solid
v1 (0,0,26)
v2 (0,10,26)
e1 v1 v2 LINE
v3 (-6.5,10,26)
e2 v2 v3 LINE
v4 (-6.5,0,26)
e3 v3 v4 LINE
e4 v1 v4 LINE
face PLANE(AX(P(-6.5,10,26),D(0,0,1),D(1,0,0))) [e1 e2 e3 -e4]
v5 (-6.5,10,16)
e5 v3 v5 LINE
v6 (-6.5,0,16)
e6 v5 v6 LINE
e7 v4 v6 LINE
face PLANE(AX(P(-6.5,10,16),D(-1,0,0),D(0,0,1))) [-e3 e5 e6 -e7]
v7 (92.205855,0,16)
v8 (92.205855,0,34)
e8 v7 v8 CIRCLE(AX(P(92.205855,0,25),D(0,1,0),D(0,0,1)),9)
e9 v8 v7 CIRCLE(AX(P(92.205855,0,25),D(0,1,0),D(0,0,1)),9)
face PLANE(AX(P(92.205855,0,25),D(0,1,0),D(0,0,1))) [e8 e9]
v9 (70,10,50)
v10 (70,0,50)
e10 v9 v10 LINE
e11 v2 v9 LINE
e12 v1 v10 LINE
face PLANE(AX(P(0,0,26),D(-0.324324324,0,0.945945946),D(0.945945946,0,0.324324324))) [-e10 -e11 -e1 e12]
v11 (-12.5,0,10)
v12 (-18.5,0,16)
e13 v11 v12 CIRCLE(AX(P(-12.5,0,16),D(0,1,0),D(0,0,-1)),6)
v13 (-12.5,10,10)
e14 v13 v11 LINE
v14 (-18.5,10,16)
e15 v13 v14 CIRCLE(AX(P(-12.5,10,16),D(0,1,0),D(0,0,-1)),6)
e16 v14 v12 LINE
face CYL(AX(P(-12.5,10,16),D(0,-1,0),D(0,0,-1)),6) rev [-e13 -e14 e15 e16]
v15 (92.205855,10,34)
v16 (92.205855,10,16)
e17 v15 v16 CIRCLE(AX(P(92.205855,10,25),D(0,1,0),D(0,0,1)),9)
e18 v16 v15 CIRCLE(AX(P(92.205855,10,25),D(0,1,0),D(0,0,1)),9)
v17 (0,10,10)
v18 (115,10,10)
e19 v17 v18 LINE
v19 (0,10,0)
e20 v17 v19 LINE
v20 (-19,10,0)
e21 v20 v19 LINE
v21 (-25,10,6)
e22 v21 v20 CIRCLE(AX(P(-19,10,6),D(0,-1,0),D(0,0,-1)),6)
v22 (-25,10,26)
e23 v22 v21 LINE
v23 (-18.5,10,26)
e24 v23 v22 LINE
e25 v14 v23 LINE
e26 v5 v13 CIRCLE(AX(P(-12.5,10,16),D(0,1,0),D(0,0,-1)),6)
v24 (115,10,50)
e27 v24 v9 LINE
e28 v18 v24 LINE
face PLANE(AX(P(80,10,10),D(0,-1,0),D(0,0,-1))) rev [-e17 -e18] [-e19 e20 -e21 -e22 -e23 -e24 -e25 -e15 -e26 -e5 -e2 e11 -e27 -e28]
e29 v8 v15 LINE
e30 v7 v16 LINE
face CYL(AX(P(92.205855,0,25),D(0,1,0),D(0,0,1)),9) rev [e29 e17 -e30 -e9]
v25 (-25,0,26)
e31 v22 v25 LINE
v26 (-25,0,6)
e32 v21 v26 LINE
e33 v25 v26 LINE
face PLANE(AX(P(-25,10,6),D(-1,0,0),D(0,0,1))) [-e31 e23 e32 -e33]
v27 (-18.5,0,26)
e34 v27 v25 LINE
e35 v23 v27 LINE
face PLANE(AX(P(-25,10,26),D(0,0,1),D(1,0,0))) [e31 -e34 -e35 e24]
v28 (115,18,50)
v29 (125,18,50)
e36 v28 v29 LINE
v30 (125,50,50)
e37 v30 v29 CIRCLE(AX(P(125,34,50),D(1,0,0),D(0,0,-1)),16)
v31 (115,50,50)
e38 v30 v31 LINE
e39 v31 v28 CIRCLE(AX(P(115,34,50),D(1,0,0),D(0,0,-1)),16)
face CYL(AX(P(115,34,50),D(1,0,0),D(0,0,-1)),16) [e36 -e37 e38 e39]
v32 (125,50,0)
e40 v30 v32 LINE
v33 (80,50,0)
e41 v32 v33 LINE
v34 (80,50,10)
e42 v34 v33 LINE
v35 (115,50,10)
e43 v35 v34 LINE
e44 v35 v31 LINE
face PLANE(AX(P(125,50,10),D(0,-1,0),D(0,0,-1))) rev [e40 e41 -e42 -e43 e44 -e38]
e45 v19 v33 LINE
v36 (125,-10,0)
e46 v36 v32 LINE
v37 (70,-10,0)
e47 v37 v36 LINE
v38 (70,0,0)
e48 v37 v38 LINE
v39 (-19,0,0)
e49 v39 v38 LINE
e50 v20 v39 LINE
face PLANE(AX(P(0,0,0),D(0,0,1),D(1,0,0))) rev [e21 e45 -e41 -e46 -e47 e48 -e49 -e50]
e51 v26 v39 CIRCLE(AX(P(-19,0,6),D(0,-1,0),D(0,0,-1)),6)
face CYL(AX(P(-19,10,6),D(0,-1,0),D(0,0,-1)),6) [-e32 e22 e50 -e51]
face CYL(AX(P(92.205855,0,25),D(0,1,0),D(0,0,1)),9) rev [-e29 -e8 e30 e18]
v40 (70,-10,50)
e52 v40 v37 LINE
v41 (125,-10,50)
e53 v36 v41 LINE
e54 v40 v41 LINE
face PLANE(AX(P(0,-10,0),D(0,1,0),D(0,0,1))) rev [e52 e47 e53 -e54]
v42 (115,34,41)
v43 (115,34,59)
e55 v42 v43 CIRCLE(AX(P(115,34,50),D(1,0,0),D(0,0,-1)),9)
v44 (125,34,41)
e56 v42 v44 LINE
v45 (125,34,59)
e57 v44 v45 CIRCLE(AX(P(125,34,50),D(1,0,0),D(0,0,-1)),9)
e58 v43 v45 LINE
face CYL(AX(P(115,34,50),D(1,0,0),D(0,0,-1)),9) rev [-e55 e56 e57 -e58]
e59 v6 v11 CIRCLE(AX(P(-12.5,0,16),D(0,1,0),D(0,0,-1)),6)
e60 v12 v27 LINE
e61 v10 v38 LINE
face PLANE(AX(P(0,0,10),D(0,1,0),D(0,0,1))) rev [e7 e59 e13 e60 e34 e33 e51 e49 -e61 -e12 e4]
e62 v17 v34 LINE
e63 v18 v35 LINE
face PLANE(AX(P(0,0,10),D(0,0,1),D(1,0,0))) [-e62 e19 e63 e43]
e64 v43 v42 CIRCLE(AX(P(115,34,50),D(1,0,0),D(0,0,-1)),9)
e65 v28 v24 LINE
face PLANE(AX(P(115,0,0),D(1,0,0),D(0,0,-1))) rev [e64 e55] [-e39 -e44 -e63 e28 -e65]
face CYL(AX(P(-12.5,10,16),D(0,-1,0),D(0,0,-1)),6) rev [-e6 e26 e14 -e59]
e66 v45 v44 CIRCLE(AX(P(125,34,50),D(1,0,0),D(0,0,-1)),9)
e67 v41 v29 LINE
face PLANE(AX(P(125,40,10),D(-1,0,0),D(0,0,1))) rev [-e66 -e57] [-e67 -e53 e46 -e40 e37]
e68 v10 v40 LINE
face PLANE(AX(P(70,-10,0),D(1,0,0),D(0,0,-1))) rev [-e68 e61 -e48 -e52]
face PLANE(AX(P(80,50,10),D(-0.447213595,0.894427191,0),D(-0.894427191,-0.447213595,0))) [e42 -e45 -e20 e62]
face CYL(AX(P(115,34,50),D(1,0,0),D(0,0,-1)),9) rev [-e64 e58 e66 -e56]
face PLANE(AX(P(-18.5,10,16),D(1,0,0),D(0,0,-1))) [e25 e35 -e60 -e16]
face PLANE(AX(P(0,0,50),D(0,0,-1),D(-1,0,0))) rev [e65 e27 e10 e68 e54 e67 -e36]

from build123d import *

# Parameters (mm, degrees)
BASE_PROFILE_DEPTH      = 10
SIDE_BLOCK_SKETCH_W     = 50
SIDE_BLOCK_SKETCH_H     = 50
SIDE_BLOCK_DEPTH        = 10
WEB_DEPTH               = 10
GUSSET_DEPTH            = 10
RAIL_SKETCH_W           = 55
RAIL_SKETCH_H           = 60
RAIL_DEPTH              = 10
POCKET_CUT_DEPTH        = 10
RELIEF_CUT_DEPTH        = 10
ARM_MOUNT_DEPTH         = 10
HOOK_ARM_DEPTH          = 10
RING_BOSS_DEPTH         = 10
BORE_18_SKETCH_R        = 9
BORE_18_DEPTH           = 10
HOOK_CUTOUT_18_SKETCH_R = 9
HOOK_CUTOUT_18_DEPTH    = 10


with BuildPart() as part:
    # Base Profile Sketch → Base Profile (new body)
    with BuildSketch(Plane.XY):
        Polygon((0, 0), (125, 0), (125, 40), (125, 50), (80, 50), (80, 10), (0, 10), align=None)
    extrude(amount=BASE_PROFILE_DEPTH)

    # Side Block Sketch → Side Block (add)
    with BuildSketch(Plane(origin=(125, 0, 0), x_dir=(0, 0, -1), z_dir=(1, 0, 0))):
        with Locations((-35, 25)):
            Rectangle(SIDE_BLOCK_SKETCH_W, SIDE_BLOCK_SKETCH_H)
    extrude(amount=-SIDE_BLOCK_DEPTH)

    # Web Sketch → Web (add)
    with BuildSketch(Plane.XZ):
        Polygon((115, 60), (70, 60), (0, 40), (0, 10), (115, 10), align=None)
    extrude(amount=-WEB_DEPTH)

    # Gusset Sketch → Gusset (add)
    with BuildSketch(Plane(origin=(0, 0, 0), x_dir=(-1, 0, 0), z_dir=(0, 0, -1))):
        Polygon((-80, 50), (0, 10), (-80, 10), align=None)
    extrude(amount=-GUSSET_DEPTH)

    # Rail Sketch → Rail (add)
    with BuildSketch(Plane.XZ):
        with Locations((97.5, 30)):
            Rectangle(RAIL_SKETCH_W, RAIL_SKETCH_H)
    extrude(amount=RAIL_DEPTH)

    # Pocket Cut Sketch → Pocket Cut (cut)
    with BuildSketch(Plane.XY.offset(60)):
        Polygon((115, 50), (125, 50), (125, -10), (70, -10), (70, 10), (115, 10), align=None)
    extrude(amount=-POCKET_CUT_DEPTH, mode=Mode.SUBTRACT)

    # Relief Cut Sketch → Relief Cut (cut)
    with BuildSketch(Plane(origin=(0, 10, 0), x_dir=(1, 0, 0), z_dir=(0, 1, 0))):
        Polygon((0, -40), (0, -10), (70, -10), (70, -60), align=None)
    extrude(amount=-RELIEF_CUT_DEPTH, mode=Mode.SUBTRACT)

    # Arm Mount Sketch → Arm Mount (add)
    with BuildSketch(Plane(origin=(0, 10, 0), x_dir=(1, 0, 0), z_dir=(0, 1, 0))):
        Polygon((70, -10), (0, -10), (0, -26), (70, -50), align=None)
    extrude(amount=-ARM_MOUNT_DEPTH)

    # Hook Arm Sketch → Hook Arm (add)
    with BuildSketch(Plane.XZ):
        with BuildLine():
            Line((0, 0), (-19, 0))
            ThreePointArc((-19, 0), (-23.242640687, 1.757359313), (-25, 6))
            Line((-25, 6), (-25, 26))
            Line((-25, 26), (-19, 26))
            Line((-19, 26), (-18.5, 26))
            Line((-18.5, 26), (-18.5, 16))
            ThreePointArc((-18.5, 16), (-12.5, 10), (-6.5, 16))
            Line((-6.5, 16), (-6.5, 26))
            Line((-6.5, 26), (-6, 26))
            Line((-6, 26), (0, 26))
            Line((0, 26), (0, 0))
        make_face()
    extrude(amount=-HOOK_ARM_DEPTH)

    # Ring Boss Sketch → Ring Boss (add)
    with BuildSketch(Plane(origin=(125, 0, 0), x_dir=(0, 0, -1), z_dir=(1, 0, 0))):
        with BuildLine():
            Line((-50, 50), (-50, 18))
            ThreePointArc((-50, 18), (-66, 34), (-50, 50))
        make_face()
    extrude(amount=-RING_BOSS_DEPTH)

    # Bore Ø18 Sketch → Bore Ø18 (cut)
    with BuildSketch(Plane(origin=(125, 0, 0), x_dir=(0, 0, -1), z_dir=(1, 0, 0))):
        with Locations((-50, 34)):
            Circle(BORE_18_SKETCH_R)
    extrude(amount=-BORE_18_DEPTH, mode=Mode.SUBTRACT)

    # Hook Cutout Ø18 Sketch → Hook Cutout Ø18 (cut)
    with BuildSketch(Plane(origin=(0, 10, 0), x_dir=(1, 0, 0), z_dir=(0, 1, 0))):
        with Locations(Location((92.205854711, -25, 0), (0, 0, 270))):
            Circle(HOOK_CUTOUT_18_SKETCH_R)
    extrude(amount=-HOOK_CUTOUT_18_DEPTH, mode=Mode.SUBTRACT)


solid = part.part
